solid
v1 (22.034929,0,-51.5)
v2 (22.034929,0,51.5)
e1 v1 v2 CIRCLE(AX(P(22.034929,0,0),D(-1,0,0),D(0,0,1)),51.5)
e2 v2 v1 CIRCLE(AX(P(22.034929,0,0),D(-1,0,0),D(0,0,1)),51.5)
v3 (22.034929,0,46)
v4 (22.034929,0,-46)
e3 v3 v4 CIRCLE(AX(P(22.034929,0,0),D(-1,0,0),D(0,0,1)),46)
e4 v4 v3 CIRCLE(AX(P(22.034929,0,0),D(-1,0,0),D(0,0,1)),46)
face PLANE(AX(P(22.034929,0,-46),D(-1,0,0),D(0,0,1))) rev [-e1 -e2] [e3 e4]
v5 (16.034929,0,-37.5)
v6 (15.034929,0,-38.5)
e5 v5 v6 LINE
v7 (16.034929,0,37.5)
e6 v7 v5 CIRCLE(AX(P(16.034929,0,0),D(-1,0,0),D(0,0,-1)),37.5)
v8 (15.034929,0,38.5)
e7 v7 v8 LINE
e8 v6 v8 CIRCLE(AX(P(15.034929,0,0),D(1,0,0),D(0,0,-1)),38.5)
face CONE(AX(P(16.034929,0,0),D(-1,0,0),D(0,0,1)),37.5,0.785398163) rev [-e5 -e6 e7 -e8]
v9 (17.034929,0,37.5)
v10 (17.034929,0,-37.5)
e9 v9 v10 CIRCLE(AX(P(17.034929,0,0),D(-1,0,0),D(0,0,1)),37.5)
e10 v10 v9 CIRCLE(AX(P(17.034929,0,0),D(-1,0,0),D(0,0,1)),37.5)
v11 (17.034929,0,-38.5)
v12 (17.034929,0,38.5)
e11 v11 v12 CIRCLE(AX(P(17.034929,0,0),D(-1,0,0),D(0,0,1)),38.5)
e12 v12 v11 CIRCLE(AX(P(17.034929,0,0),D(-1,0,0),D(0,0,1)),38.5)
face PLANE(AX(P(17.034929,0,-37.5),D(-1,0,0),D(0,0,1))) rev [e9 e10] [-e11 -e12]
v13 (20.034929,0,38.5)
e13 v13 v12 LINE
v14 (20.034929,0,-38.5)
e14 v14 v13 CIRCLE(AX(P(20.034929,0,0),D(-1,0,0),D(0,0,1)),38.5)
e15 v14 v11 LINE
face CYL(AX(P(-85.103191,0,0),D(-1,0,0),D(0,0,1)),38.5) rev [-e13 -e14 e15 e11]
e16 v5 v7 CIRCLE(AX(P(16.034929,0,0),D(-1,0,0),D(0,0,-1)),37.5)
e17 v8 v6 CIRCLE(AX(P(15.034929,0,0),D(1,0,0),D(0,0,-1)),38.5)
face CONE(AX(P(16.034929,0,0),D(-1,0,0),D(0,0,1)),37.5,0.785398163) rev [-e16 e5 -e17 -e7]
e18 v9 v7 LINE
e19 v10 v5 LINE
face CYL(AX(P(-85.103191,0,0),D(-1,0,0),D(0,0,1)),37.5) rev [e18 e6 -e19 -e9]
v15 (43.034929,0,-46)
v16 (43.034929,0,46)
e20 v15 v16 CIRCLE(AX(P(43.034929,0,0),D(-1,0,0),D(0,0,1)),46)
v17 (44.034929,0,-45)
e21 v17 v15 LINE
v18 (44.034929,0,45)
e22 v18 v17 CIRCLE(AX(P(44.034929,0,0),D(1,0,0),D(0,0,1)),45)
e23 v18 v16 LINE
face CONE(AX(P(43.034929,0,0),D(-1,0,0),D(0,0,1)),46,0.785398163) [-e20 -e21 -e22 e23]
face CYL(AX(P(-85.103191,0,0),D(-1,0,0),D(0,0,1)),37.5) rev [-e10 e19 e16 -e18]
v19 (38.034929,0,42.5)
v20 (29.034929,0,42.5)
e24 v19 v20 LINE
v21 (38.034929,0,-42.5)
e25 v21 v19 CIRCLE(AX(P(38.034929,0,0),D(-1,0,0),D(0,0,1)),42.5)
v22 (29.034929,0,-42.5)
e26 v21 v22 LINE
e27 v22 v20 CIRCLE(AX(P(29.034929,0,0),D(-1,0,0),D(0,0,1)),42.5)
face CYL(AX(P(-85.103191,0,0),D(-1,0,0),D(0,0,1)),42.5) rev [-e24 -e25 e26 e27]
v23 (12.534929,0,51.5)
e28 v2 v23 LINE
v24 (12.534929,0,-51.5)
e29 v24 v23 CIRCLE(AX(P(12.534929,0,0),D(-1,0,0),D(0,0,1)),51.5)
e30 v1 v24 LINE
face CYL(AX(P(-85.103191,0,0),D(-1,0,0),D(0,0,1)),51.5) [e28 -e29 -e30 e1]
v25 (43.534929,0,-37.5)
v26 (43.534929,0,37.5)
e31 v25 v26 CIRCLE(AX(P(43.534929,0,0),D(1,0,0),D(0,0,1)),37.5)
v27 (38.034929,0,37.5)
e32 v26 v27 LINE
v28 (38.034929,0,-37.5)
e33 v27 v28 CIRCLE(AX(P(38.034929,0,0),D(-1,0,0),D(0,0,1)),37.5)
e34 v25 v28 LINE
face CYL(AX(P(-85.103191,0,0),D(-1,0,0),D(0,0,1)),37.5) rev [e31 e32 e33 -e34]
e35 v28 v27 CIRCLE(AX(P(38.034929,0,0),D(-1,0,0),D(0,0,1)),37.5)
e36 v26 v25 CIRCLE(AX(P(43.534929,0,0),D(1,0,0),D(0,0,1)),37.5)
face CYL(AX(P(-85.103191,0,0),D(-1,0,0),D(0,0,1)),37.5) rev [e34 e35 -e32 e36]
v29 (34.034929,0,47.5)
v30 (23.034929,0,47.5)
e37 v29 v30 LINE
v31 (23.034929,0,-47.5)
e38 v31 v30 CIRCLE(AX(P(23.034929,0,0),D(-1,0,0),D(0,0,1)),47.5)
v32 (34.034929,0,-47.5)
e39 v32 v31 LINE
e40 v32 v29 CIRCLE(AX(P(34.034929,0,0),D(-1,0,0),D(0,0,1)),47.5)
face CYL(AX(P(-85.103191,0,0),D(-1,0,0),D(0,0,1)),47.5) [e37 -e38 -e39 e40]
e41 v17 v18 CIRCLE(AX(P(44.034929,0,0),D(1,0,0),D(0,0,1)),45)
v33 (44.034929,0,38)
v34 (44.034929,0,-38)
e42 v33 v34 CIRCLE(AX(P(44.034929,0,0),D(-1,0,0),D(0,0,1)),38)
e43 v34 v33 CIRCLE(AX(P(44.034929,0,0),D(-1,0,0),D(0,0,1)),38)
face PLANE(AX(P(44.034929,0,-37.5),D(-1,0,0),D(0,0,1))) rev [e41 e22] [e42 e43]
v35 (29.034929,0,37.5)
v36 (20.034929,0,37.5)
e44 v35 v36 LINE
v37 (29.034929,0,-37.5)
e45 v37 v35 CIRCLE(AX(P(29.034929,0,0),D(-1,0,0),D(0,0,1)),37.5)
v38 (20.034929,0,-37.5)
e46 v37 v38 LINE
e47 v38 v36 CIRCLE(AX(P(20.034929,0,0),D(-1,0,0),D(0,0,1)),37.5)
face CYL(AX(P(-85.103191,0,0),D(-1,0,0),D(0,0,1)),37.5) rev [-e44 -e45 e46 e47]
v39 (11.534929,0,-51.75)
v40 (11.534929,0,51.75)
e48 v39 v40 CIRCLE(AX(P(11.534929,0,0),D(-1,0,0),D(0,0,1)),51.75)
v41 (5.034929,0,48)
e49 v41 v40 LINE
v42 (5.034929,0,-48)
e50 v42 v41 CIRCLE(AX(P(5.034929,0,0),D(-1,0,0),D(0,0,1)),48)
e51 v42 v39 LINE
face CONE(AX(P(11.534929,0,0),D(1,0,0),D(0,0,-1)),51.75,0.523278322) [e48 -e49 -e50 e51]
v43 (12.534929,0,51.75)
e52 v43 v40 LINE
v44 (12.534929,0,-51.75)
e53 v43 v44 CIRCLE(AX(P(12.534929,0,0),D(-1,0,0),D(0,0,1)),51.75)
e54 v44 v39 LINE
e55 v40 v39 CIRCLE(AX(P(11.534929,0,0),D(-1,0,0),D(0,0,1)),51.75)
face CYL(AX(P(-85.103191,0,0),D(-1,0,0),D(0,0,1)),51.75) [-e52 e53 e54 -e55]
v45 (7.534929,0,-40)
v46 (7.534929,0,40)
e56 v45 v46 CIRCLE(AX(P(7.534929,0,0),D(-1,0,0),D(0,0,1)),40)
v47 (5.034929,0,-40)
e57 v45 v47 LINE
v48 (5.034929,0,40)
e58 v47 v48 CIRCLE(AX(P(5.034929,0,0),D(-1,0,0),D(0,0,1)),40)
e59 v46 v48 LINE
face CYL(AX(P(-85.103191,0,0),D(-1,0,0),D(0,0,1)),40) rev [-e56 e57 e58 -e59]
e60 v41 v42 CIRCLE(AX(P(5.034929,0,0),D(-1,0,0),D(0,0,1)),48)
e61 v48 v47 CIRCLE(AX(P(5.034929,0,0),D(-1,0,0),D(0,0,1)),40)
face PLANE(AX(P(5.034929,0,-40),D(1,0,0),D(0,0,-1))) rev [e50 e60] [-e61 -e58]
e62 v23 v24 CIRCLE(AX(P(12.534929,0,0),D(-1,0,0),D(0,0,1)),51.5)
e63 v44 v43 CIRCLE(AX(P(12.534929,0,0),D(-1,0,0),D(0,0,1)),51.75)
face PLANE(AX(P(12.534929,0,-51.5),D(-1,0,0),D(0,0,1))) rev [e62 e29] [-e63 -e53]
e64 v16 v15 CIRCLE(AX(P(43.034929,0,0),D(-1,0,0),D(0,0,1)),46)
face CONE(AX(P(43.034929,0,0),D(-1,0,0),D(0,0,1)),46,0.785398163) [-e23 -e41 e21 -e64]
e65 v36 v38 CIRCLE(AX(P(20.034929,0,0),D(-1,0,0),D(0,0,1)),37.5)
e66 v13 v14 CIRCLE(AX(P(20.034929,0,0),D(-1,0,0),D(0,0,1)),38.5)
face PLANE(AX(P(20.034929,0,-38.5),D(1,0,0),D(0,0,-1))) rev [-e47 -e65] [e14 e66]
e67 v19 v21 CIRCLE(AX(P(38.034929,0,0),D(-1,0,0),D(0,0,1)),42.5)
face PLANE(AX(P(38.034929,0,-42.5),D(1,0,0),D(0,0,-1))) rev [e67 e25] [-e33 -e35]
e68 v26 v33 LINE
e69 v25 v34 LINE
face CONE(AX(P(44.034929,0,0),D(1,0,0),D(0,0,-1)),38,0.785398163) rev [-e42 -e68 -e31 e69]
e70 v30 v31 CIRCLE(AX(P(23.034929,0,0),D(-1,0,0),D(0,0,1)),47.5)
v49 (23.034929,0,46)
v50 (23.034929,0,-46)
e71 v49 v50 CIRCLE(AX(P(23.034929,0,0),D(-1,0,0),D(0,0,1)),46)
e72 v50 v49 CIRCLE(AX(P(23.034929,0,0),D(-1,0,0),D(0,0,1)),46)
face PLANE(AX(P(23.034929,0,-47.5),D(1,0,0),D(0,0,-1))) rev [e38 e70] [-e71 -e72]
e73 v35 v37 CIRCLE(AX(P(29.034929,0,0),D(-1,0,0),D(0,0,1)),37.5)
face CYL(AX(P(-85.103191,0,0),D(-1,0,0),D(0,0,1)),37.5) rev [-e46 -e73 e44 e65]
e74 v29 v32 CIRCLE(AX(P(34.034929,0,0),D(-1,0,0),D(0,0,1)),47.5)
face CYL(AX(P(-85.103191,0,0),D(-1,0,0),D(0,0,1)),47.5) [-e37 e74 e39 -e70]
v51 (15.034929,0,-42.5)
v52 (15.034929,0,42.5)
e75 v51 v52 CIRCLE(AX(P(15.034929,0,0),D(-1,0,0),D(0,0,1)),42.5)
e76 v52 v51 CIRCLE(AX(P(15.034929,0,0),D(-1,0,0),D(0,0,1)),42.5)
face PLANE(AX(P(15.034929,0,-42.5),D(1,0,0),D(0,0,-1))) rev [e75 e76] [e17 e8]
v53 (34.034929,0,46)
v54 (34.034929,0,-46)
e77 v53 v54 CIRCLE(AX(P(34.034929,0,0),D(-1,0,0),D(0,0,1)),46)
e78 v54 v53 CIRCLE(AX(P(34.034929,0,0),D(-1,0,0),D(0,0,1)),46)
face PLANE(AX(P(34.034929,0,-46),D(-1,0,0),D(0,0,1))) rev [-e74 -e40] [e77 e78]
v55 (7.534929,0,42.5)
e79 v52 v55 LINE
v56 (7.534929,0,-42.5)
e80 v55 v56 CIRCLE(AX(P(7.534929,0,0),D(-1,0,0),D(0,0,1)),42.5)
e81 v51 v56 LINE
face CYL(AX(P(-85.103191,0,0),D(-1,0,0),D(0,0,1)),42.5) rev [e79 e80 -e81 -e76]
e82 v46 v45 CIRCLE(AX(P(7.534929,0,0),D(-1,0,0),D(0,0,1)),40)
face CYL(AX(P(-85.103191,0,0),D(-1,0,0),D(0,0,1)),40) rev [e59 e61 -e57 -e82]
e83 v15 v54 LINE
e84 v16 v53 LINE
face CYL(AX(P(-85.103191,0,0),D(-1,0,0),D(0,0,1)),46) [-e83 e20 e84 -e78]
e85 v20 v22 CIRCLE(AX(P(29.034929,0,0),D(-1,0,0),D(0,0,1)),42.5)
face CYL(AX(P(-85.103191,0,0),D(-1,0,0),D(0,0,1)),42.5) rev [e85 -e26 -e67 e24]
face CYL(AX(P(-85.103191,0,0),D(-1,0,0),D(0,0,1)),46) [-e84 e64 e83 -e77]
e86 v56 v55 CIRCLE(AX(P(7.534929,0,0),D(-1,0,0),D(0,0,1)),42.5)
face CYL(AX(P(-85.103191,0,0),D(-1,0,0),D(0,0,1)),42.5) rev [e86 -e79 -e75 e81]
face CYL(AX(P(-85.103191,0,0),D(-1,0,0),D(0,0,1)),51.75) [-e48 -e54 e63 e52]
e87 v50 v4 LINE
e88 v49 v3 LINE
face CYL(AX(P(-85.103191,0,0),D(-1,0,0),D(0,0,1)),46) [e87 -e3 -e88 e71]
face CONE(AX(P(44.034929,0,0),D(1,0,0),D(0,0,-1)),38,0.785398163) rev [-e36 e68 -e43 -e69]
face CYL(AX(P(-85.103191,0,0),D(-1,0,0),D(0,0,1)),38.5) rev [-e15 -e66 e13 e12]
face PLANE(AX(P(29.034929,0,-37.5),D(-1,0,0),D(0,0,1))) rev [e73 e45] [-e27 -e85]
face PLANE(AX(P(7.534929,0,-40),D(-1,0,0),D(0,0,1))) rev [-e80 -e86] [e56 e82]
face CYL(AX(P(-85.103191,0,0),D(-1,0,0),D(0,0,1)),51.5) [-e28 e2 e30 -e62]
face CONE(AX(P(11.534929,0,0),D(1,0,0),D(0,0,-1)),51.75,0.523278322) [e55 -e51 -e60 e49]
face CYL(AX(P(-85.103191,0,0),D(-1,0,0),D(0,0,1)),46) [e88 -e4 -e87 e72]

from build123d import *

# Parameters (mm, degrees)
CHAMFER_1_SIZE = 1
CHAMFER_2_SIZE = 0.5
CHAMFER_3_SIZE = 1


with BuildPart() as part:
    # 草图1 → 旋转1 (revolve)
    with BuildSketch(Plane(origin=(0, 0, 0), x_dir=(1, 0, 0), z_dir=(0, 1, 0)), mode=Mode.PRIVATE) as revolve_1_sk:
        Polygon((5.034928566, 40), (7.534928566, 40), (7.534928566, 42.5), (15.034928566, 42.5), (15.034928566, 37.5), (17.034928566, 37.5), (17.034928566, 38.5), (20.034928566, 38.5), (20.034928566, 37.5), (29.034928566, 37.5), (29.034928566, 42.5), (38.034928566, 42.5), (38.034928566, 37.5), (44.034928566, 37.5), (44.034928566, 46), (34.034928566, 46), (34.034928566, 47.5), (23.034928566, 47.5), (23.034928566, 46), (22.034928566, 46), (22.034928566, 51.5), (12.534928566, 51.5), (12.534928566, 51.75), (11.534928566, 51.75), (5.034928566, 48), align=None)
    revolve(revolve_1_sk.sketch.rotate(Axis((-85.103190975, 0, 0), (1, 0, 0)), 180), axis=Axis((-85.103190975, 0, 0), (1, 0, 0)))

    # 倒角1
    chamfer_1_edges = [part.edges().sort_by_distance(p)[0] for p in [
        (44.034928566, 0, -46),
    ]]
    chamfer(chamfer_1_edges, length=CHAMFER_1_SIZE)

    # 倒角2
    chamfer_2_edges = [part.edges().sort_by_distance(p)[0] for p in [
        (44.034928566, 0, -37.5),
    ]]
    chamfer(chamfer_2_edges, length=CHAMFER_2_SIZE)

    # 倒角3
    chamfer_3_edges = [part.edges().sort_by_distance(p)[0] for p in [
        (15.034928566, 0, -37.5),
    ]]
    chamfer(chamfer_3_edges, length=CHAMFER_3_SIZE)


solid = part.part
